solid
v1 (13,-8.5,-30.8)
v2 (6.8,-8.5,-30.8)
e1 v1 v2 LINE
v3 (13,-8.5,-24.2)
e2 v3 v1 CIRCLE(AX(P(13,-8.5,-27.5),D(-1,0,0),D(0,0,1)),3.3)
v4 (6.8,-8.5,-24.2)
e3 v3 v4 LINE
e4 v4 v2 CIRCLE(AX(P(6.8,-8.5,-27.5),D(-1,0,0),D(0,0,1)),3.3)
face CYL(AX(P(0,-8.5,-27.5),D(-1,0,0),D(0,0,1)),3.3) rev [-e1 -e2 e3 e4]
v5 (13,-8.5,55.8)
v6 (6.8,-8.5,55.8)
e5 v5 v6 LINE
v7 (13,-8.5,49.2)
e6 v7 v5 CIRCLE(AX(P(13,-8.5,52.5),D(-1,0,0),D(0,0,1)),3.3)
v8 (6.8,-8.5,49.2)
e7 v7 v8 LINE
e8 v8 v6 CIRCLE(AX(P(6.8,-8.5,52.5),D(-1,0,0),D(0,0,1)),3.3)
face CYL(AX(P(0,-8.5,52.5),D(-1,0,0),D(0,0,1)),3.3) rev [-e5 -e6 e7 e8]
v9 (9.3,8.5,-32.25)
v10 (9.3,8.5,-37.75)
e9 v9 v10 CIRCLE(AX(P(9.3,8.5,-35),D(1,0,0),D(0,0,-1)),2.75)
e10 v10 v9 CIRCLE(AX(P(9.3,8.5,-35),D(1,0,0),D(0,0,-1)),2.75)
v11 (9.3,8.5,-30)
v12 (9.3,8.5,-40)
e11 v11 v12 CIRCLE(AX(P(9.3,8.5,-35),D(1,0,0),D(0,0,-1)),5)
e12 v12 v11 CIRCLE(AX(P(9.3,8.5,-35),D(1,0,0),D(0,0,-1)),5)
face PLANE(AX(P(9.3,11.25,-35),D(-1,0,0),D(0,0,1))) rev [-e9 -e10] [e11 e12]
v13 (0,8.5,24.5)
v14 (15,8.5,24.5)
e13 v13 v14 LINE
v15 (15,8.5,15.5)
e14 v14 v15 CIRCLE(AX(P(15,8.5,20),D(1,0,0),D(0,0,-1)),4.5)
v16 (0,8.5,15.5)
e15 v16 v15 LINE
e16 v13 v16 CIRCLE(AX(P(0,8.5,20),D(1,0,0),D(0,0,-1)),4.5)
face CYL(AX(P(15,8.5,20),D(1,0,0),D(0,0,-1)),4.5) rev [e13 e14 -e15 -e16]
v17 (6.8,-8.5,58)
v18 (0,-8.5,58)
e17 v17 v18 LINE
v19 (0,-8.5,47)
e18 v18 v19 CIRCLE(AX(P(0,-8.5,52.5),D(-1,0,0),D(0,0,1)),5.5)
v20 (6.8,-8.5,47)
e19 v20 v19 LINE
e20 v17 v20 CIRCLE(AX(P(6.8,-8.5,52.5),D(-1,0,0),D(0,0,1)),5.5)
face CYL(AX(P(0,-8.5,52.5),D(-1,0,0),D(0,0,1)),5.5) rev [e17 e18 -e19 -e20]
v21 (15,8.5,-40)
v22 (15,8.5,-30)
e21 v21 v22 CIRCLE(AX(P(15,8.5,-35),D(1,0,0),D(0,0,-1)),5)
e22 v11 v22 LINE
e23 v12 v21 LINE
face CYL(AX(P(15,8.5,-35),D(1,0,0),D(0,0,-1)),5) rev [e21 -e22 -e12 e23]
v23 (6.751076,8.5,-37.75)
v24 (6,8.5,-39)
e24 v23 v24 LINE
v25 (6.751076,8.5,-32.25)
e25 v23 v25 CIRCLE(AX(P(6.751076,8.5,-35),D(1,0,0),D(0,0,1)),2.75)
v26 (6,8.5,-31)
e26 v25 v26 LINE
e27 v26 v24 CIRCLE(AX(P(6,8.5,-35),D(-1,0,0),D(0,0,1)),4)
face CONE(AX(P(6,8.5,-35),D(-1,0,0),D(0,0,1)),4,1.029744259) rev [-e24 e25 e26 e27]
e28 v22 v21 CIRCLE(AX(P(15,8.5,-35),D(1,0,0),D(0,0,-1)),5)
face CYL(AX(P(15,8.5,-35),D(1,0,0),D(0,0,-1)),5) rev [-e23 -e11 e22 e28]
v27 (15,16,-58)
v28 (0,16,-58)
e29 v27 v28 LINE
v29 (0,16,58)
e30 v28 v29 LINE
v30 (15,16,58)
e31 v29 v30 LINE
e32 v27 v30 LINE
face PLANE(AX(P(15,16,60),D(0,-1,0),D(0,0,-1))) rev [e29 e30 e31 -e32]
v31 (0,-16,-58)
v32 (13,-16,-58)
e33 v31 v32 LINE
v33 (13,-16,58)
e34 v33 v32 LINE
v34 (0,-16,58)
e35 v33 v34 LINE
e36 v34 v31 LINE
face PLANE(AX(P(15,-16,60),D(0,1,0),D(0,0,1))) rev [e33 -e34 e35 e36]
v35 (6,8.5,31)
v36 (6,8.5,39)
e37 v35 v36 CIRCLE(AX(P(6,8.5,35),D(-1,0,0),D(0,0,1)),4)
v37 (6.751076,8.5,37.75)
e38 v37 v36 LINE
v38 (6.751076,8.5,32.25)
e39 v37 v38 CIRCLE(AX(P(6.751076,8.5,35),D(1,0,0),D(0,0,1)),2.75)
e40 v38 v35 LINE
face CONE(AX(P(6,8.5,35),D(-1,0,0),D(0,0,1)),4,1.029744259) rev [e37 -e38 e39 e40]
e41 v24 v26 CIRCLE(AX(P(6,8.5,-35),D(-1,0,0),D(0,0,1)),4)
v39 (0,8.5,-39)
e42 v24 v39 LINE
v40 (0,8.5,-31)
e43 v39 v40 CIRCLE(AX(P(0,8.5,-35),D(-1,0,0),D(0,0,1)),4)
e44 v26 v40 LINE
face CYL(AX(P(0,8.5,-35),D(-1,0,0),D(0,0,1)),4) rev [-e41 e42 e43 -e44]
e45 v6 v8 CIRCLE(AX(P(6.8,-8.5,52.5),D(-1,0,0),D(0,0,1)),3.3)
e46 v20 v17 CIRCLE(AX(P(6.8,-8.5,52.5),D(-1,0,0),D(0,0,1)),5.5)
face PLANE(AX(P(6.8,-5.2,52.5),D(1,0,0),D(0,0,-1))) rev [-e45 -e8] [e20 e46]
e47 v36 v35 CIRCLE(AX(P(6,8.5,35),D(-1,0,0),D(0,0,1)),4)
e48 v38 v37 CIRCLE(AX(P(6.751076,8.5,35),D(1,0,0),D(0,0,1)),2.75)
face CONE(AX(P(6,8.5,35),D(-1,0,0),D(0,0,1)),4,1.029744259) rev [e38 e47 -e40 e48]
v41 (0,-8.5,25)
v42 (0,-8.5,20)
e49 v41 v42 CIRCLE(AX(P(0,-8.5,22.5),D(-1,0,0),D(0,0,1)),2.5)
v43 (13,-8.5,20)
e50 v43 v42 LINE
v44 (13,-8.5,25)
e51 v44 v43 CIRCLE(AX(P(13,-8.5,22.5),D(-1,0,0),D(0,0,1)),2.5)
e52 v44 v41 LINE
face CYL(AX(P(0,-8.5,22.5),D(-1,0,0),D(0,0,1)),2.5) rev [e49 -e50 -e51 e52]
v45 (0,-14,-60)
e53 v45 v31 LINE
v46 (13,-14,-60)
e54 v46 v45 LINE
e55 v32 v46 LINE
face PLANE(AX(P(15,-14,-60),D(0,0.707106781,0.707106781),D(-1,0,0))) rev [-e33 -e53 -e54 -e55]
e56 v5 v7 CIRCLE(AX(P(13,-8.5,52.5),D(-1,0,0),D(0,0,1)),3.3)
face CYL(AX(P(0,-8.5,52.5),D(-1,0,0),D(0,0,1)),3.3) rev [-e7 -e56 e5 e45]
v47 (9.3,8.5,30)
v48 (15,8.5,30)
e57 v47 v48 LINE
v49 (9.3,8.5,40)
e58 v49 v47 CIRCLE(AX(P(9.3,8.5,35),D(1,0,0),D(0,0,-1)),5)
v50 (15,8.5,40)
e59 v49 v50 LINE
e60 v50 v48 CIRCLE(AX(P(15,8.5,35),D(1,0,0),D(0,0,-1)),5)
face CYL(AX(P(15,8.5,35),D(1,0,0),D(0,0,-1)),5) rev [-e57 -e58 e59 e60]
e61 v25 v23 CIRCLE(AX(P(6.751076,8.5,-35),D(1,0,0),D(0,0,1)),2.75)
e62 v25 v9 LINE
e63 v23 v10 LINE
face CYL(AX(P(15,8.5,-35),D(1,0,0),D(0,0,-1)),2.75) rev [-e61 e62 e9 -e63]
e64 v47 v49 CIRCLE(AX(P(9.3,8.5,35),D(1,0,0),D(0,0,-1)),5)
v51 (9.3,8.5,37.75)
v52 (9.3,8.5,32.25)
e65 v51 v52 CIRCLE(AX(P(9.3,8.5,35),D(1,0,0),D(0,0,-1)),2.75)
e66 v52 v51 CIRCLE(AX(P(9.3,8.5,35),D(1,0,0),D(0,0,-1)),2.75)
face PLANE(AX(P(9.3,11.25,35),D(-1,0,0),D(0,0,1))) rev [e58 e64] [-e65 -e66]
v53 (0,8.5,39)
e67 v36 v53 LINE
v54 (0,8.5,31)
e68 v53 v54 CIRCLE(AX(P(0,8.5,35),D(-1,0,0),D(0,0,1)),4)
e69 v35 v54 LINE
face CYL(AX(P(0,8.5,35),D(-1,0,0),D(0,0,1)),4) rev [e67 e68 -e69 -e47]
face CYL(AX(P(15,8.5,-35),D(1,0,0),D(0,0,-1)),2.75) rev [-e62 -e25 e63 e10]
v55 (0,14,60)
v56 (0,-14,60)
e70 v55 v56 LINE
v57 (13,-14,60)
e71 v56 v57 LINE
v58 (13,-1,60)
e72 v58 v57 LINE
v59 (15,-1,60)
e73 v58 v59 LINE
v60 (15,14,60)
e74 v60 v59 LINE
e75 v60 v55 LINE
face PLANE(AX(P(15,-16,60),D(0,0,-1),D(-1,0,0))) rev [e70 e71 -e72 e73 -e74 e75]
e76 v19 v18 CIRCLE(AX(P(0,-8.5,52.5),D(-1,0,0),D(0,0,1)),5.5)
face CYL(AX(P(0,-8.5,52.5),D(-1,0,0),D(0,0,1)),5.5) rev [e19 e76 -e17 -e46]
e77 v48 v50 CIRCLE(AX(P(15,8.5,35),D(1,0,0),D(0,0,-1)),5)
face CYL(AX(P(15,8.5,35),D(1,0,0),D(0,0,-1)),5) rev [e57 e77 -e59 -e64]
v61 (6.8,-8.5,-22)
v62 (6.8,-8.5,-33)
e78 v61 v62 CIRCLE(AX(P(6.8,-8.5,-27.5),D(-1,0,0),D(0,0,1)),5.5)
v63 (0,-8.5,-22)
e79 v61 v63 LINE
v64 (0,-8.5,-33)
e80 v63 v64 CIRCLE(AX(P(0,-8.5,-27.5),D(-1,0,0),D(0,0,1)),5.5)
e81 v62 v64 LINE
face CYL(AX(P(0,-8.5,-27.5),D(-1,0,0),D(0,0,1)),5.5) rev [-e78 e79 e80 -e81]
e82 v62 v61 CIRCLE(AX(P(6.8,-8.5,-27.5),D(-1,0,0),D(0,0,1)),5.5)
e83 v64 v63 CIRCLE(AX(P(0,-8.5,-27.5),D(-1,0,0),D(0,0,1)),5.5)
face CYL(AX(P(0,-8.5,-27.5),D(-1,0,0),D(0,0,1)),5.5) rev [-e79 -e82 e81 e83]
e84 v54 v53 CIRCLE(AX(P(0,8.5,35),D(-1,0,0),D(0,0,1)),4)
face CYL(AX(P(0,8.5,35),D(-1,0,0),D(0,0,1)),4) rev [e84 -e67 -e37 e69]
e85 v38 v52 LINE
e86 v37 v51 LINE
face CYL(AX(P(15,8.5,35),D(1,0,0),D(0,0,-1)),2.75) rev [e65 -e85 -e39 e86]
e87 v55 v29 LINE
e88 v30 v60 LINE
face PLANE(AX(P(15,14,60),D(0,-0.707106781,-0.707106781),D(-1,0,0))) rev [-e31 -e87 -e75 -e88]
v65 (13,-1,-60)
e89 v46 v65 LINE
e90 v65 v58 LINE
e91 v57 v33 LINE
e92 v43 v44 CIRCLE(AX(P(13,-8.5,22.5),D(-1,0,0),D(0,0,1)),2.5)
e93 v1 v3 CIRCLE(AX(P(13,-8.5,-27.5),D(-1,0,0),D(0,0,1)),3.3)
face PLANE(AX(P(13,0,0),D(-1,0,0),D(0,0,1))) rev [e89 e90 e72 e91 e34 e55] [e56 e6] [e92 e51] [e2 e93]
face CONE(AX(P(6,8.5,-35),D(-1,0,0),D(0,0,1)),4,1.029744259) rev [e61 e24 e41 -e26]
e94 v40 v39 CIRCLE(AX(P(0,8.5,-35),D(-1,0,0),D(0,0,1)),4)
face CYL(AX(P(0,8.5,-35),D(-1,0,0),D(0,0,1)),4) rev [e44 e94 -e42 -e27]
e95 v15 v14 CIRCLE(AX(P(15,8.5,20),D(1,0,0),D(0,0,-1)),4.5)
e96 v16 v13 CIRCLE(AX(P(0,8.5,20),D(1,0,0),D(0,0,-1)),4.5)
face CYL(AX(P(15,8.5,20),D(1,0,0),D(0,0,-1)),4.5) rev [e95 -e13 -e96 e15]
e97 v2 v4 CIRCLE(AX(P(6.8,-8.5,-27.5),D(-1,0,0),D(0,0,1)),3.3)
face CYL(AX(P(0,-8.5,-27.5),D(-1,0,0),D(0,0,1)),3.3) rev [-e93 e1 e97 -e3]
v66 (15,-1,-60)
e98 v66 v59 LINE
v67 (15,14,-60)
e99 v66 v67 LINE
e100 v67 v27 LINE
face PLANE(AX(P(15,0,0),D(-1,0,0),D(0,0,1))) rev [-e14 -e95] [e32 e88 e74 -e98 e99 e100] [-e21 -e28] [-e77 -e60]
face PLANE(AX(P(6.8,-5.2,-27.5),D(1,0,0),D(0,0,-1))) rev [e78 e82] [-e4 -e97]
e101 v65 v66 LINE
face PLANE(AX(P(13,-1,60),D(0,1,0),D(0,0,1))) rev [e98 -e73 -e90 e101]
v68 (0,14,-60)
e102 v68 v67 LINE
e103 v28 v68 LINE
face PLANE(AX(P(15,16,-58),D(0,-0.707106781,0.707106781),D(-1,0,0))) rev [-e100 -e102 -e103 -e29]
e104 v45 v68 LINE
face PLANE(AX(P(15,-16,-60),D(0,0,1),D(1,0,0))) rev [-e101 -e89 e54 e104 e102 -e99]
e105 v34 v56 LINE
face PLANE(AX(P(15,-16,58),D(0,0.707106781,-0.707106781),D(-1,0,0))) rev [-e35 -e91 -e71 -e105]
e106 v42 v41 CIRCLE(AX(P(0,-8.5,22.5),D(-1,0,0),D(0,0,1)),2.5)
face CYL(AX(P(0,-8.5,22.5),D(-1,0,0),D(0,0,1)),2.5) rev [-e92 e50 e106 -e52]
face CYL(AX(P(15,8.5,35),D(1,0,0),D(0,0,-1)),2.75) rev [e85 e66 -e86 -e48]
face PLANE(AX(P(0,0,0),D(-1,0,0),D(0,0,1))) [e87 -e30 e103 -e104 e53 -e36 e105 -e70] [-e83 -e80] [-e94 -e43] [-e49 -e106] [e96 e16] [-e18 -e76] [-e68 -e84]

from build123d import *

# Parameters (mm, degrees)
SKETCH1_W                                            = 120
SKETCH1_H                                            = 32
BOSS_EXTRUDE1_DEPTH                                  = 15
SKETCH2_W                                            = 120
SKETCH2_H                                            = 15
CUT_EXTRUDE1_DEPTH                                   = 2
F_8_0MM_BLIND_HOLE_1_D                               = 8
F_8_0MM_BLIND_HOLE_1_DEPTH                           = 6
F_8_0MM_BLIND_HOLE_1_TIP                             = 2.403442476
M8_CLEARANCE_HOLE1_D                                 = 9
CHAMFER1_SIZE                                        = 2
CBORE_FOR_M5_HEXAGON_SOCKET_HEAD_CAP_SCR_D           = 5.5
CBORE_FOR_M5_HEXAGON_SOCKET_HEAD_CAP_SCR_CBORE_D     = 10
CBORE_FOR_M5_HEXAGON_SOCKET_HEAD_CAP_SCR_CBORE_DEPTH = 5.7
CBORE_FOR_M6_HEXAGON_SOCKET_HEAD_CAP_SCR_D           = 6.6
CBORE_FOR_M6_HEXAGON_SOCKET_HEAD_CAP_SCR_CBORE_D     = 11
CBORE_FOR_M6_HEXAGON_SOCKET_HEAD_CAP_SCR_CBORE_DEPTH = 6.8
F_5_0MM_BLIND_HOLE_1_D                               = 5


with BuildPart() as part:
    # Sketch1 → Boss-Extrude1 (new body)
    with BuildSketch(Plane(origin=(0, 0, 0), x_dir=(0, 0, -1), z_dir=(1, 0, 0))):
        Rectangle(SKETCH1_W, SKETCH1_H)
    extrude(amount=BOSS_EXTRUDE1_DEPTH)

    # Sketch2 → Cut-Extrude1 (cut)
    with BuildSketch(Plane(origin=(15, 0, 0), x_dir=(0, 0, -1), z_dir=(1, 0, 0))):
        with Locations((0, -8.5)):
            Rectangle(SKETCH2_W, SKETCH2_H)
    extrude(amount=-CUT_EXTRUDE1_DEPTH, mode=Mode.SUBTRACT)

    # Ø8.0mm blind hole 1
    with Locations(Plane.ZY):
        with Locations((35, 8.5), (-35, 8.5)):
            Hole(F_8_0MM_BLIND_HOLE_1_D / 2, depth=F_8_0MM_BLIND_HOLE_1_DEPTH)
            with Locations((0, 0, -(F_8_0MM_BLIND_HOLE_1_DEPTH + F_8_0MM_BLIND_HOLE_1_TIP / 2))):  # 118° drill point
                Cone(0, F_8_0MM_BLIND_HOLE_1_D / 2, F_8_0MM_BLIND_HOLE_1_TIP, mode=Mode.SUBTRACT)

    # M8 Clearance Hole1 (through all)
    with Locations(Plane(origin=(15, 0, 0), x_dir=(0, 0, -1), z_dir=(1, 0, 0))):
        with Locations((-20, 8.5)):
            Hole(M8_CLEARANCE_HOLE1_D / 2)

    # Chamfer1
    chamfer1_edges = [part.edges().sort_by_distance(p)[0] for p in [
        (6.5, -16, -60),
        (6.5, -16, 60),
        (7.5, 16, 60),
        (7.5, 16, -60),
    ]]
    chamfer(chamfer1_edges, length=CHAMFER1_SIZE)

    # CBORE for M5 Hexagon socket head cap screws1 (through all)
    with Locations(Plane(origin=(15, 0, 0), x_dir=(0, 0, -1), z_dir=(1, 0, 0))):
        with Locations((-35, 8.5), (35, 8.5)):
            CounterBoreHole(CBORE_FOR_M5_HEXAGON_SOCKET_HEAD_CAP_SCR_D / 2, CBORE_FOR_M5_HEXAGON_SOCKET_HEAD_CAP_SCR_CBORE_D / 2, CBORE_FOR_M5_HEXAGON_SOCKET_HEAD_CAP_SCR_CBORE_DEPTH)

    # CBORE for M6 Hexagon socket head cap screws1 (through all)
    with Locations(Plane.ZY):
        with Locations((-27.5, -8.5), (52.5, -8.5)):
            CounterBoreHole(CBORE_FOR_M6_HEXAGON_SOCKET_HEAD_CAP_SCR_D / 2, CBORE_FOR_M6_HEXAGON_SOCKET_HEAD_CAP_SCR_CBORE_D / 2, CBORE_FOR_M6_HEXAGON_SOCKET_HEAD_CAP_SCR_CBORE_DEPTH)

    # Ø5.0mm blind hole 1 (through all)
    with Locations(Plane.ZY):
        with Locations((22.5, -8.5)):
            Hole(F_5_0MM_BLIND_HOLE_1_D / 2)


solid = part.part
